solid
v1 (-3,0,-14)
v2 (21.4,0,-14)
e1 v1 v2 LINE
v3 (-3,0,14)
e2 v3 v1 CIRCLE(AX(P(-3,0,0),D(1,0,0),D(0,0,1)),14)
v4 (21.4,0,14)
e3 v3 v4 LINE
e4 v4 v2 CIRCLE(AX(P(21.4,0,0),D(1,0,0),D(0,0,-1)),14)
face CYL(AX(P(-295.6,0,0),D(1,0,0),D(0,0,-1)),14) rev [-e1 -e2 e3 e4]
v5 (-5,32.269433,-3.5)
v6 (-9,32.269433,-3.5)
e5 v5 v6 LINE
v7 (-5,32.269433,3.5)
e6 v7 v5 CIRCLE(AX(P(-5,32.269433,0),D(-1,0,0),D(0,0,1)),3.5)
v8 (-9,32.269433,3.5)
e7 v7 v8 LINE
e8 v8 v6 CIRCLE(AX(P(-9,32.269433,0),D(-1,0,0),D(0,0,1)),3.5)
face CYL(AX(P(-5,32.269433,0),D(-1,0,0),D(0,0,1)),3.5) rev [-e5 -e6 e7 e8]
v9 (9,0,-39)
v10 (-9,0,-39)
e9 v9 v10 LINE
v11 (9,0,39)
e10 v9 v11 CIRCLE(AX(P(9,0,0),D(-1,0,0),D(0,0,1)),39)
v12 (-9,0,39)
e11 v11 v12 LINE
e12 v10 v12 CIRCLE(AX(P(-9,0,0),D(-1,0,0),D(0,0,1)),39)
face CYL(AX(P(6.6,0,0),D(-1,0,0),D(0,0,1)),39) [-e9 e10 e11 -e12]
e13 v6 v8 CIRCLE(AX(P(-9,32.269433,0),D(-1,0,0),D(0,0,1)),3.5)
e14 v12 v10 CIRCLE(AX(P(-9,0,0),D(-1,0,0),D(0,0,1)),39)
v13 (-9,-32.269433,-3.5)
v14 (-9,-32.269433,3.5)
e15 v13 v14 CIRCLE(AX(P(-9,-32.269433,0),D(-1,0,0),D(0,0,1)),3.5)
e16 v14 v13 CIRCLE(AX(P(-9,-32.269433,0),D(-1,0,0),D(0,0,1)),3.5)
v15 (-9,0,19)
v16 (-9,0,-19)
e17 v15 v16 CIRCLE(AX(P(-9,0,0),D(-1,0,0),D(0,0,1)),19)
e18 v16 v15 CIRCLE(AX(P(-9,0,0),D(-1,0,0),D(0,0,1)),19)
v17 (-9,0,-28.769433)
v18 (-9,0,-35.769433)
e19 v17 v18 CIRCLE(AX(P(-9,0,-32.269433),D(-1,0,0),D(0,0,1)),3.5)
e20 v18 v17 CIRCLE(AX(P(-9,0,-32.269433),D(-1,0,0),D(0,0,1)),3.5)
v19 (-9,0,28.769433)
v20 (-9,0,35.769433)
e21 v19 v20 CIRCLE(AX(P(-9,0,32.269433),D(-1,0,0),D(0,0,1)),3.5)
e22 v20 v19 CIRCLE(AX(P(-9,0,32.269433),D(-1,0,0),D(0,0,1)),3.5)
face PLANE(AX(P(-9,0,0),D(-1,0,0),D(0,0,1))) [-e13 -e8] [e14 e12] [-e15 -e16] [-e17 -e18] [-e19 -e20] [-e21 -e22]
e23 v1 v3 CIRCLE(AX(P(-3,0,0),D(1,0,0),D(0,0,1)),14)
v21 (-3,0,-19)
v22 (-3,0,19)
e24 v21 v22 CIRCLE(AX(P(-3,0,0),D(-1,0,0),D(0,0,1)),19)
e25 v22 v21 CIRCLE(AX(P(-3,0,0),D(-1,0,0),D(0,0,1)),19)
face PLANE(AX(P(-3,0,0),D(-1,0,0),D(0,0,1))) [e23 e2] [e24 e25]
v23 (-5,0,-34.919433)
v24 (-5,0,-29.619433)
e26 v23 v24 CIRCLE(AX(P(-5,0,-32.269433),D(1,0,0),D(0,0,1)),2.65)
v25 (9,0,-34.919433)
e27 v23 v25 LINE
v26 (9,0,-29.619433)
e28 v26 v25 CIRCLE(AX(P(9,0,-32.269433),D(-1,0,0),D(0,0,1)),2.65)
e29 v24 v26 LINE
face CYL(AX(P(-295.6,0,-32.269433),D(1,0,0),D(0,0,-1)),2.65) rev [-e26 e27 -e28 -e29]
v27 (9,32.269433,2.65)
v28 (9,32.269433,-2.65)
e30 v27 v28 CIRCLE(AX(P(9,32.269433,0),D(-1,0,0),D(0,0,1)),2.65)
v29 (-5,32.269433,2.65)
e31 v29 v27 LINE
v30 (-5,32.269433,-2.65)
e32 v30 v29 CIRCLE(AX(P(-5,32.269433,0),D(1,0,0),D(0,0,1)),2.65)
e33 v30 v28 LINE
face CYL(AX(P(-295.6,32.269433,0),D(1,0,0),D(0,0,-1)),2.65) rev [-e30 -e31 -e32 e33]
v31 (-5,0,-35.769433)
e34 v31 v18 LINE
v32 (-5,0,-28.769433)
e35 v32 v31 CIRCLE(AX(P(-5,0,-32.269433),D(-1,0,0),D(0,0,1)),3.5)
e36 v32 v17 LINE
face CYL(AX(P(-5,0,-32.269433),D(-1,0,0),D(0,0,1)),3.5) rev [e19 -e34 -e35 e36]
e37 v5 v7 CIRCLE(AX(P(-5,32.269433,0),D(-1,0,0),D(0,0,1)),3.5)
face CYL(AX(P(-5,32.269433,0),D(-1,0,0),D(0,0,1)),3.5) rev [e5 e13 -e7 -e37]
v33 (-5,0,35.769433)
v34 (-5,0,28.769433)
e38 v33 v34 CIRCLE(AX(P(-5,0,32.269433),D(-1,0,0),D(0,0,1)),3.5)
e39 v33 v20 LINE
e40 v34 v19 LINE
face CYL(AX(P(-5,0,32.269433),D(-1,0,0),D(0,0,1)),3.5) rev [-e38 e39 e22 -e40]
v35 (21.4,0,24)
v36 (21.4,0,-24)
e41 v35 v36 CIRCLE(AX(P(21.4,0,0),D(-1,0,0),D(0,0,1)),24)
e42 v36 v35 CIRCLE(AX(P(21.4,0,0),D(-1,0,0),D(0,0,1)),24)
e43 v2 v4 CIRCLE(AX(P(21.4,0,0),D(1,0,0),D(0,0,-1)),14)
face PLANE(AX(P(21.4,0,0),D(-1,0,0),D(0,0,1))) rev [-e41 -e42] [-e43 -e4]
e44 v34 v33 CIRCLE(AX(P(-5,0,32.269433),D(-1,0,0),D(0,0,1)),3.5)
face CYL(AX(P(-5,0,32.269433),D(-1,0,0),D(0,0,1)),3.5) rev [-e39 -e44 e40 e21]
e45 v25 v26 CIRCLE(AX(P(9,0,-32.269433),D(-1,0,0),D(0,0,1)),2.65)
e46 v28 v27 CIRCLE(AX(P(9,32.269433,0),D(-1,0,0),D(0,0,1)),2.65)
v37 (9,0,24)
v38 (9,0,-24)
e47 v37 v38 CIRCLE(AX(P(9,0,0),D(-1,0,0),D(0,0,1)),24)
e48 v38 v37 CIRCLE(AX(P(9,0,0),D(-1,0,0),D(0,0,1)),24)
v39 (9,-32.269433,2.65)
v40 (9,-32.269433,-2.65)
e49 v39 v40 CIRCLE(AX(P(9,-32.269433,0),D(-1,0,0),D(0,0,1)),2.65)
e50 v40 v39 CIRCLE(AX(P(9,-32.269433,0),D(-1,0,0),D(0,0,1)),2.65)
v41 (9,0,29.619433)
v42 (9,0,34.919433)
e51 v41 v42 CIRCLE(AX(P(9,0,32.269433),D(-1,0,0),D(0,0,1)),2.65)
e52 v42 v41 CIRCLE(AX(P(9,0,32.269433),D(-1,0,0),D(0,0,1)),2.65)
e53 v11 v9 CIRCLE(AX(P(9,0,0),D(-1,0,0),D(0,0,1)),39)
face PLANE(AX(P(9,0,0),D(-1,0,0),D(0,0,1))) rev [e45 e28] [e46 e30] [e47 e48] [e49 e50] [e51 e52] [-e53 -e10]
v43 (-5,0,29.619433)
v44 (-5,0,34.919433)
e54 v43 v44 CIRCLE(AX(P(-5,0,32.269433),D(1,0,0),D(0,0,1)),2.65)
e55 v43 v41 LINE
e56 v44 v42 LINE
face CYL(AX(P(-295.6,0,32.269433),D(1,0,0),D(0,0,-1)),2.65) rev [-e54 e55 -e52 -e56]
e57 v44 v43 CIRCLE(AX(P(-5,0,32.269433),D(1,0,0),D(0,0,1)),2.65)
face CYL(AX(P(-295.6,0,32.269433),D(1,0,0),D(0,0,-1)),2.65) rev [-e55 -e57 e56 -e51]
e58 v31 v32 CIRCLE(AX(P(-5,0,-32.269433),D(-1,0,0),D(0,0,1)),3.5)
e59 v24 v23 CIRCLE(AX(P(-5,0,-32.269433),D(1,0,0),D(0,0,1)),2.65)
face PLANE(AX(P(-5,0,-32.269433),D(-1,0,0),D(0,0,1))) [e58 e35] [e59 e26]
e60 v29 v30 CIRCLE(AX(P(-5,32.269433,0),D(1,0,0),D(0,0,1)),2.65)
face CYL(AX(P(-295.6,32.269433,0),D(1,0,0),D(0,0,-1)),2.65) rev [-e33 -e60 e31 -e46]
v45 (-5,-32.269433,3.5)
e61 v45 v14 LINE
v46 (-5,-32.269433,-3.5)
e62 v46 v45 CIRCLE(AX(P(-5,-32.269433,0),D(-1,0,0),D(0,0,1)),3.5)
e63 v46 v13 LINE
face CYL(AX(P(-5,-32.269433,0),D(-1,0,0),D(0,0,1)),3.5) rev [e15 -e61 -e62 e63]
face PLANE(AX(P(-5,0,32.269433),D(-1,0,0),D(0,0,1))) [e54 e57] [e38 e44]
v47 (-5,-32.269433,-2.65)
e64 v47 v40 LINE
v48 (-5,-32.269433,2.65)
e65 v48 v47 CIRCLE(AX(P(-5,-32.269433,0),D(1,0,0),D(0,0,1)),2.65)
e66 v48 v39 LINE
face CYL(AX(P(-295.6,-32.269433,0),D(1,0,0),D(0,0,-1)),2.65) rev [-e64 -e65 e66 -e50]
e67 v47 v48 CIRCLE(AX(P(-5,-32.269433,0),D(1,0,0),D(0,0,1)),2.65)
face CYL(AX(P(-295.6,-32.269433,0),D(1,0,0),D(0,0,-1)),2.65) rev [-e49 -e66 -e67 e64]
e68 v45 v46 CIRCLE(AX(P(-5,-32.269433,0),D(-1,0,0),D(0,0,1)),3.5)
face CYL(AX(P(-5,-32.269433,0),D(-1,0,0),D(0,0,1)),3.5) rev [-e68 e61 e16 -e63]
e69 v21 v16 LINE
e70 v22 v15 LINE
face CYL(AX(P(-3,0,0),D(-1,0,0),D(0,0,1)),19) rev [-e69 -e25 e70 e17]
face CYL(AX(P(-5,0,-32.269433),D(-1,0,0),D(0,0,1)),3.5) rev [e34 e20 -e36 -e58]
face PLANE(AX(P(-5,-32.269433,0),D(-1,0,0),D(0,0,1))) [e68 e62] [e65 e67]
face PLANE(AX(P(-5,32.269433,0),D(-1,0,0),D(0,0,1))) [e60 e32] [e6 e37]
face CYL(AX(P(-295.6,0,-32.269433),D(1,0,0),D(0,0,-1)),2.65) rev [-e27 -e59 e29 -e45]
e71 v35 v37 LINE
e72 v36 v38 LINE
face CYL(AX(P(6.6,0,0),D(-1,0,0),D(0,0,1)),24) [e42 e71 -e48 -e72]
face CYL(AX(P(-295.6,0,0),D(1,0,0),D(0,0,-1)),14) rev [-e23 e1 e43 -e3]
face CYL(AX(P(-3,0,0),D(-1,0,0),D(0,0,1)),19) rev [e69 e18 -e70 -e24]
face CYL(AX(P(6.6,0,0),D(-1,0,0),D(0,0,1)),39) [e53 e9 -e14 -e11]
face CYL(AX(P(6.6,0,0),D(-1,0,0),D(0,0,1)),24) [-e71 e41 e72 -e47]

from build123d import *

# Parameters (mm, degrees)
HUB_PROFILE_SKETCH_W        = 5
HUB_PROFILE_SKETCH_H        = 20
HUB_PROFILE_SKETCH_W_2      = 4
MOUNTING_HOLES_SKETCH_R     = 14
MOUNTING_HOLES_SKETCH_R_2   = 2.65
MOUNTING_HOLES_4X_5_3_DEPTH = 317
SLOT_SKETCH_R               = 3.5
SLOT_7MM_X_4_DEEP_DEPTH     = 4
RECESS_SKETCH_R             = 19
RECESS_38_X_6_DEEP_DEPTH    = 6


with BuildPart() as part:
    # Hub Profile Sketch → Flanged Hub Body (revolve)
    with BuildSketch(Plane.XY, mode=Mode.PRIVATE) as flanged_hub_body_sk:
        with BuildLine():
            Line((-5, -19), (0, -19))
            Line((0, -19), (4.6, -19))
            ThreePointArc((4.6, -19), (6.014213562, -18.414213562), (6.6, -17))
            Line((6.6, -17), (6.6, 0))
            Line((6.6, 0), (-9, 0))
            Line((-9, 0), (-9, -19))
            Line((-9, -19), (-5, -19))
        make_face()
        with BuildLine():
            Line((9, -39), (9, -24))
            Line((9, -24), (21.4, -24))
            Line((21.4, -24), (21.4, 0))
            Line((21.4, 0), (6.6, 0))
            Line((6.6, 0), (6.6, -17))
            ThreePointArc((6.6, -17), (6.014213562, -18.414213562), (4.6, -19))
            Line((4.6, -19), (0, -19))
            Line((0, -19), (0, -39))
            Line((0, -39), (9, -39))
        make_face()
        with Locations((-2.5, -29)):
            Rectangle(HUB_PROFILE_SKETCH_W, HUB_PROFILE_SKETCH_H)
        with Locations((-7, -29)):
            Rectangle(HUB_PROFILE_SKETCH_W_2, HUB_PROFILE_SKETCH_H)
    revolve(flanged_hub_body_sk.sketch.rotate(Axis((6.6, 0, 0), (1, 0, 0)), 270), axis=Axis((6.6, 0, 0), (1, 0, 0)))

    # Mounting Holes Sketch → Mounting Holes 4xØ5.3 (cut)
    with BuildSketch(Plane(origin=(21.4, 0, 0), x_dir=(0, 0, -1), z_dir=(1, 0, 0))):
        Circle(MOUNTING_HOLES_SKETCH_R)
        with Locations(Location((0, 32.26943336, 0), (0, 0, 180))):
            Circle(MOUNTING_HOLES_SKETCH_R_2)
        with Locations(Location((32.26943336, 0, 0), (0, 0, 180))):
            Circle(MOUNTING_HOLES_SKETCH_R_2)
        with Locations(Location((0, -32.26943336, 0), (0, 0, 180))):
            Circle(MOUNTING_HOLES_SKETCH_R_2)
        with Locations(Location((-32.26943336, 0, 0), (0, 0, 180))):
            Circle(MOUNTING_HOLES_SKETCH_R_2)
    extrude(amount=-MOUNTING_HOLES_4X_5_3_DEPTH, mode=Mode.SUBTRACT)

    # Slot Sketch → Slot 7mm x 4 Deep (cut)
    with BuildSketch(Plane.ZY.offset(9)):
        with Locations((0, 32.26943336)):
            Circle(SLOT_SKETCH_R)
        with Locations((-32.26943336, 0)):
            Circle(SLOT_SKETCH_R)
        with Locations((0, -32.26943336)):
            Circle(SLOT_SKETCH_R)
        with Locations((32.26943336, 0)):
            Circle(SLOT_SKETCH_R)
    extrude(amount=-SLOT_7MM_X_4_DEEP_DEPTH, mode=Mode.SUBTRACT)

    # Recess Sketch → Recess Ø38 x 6 Deep (cut)
    with BuildSketch(Plane.ZY.offset(9)):
        Circle(RECESS_SKETCH_R)
    extrude(amount=-RECESS_38_X_6_DEEP_DEPTH, mode=Mode.SUBTRACT)


solid = part.part
